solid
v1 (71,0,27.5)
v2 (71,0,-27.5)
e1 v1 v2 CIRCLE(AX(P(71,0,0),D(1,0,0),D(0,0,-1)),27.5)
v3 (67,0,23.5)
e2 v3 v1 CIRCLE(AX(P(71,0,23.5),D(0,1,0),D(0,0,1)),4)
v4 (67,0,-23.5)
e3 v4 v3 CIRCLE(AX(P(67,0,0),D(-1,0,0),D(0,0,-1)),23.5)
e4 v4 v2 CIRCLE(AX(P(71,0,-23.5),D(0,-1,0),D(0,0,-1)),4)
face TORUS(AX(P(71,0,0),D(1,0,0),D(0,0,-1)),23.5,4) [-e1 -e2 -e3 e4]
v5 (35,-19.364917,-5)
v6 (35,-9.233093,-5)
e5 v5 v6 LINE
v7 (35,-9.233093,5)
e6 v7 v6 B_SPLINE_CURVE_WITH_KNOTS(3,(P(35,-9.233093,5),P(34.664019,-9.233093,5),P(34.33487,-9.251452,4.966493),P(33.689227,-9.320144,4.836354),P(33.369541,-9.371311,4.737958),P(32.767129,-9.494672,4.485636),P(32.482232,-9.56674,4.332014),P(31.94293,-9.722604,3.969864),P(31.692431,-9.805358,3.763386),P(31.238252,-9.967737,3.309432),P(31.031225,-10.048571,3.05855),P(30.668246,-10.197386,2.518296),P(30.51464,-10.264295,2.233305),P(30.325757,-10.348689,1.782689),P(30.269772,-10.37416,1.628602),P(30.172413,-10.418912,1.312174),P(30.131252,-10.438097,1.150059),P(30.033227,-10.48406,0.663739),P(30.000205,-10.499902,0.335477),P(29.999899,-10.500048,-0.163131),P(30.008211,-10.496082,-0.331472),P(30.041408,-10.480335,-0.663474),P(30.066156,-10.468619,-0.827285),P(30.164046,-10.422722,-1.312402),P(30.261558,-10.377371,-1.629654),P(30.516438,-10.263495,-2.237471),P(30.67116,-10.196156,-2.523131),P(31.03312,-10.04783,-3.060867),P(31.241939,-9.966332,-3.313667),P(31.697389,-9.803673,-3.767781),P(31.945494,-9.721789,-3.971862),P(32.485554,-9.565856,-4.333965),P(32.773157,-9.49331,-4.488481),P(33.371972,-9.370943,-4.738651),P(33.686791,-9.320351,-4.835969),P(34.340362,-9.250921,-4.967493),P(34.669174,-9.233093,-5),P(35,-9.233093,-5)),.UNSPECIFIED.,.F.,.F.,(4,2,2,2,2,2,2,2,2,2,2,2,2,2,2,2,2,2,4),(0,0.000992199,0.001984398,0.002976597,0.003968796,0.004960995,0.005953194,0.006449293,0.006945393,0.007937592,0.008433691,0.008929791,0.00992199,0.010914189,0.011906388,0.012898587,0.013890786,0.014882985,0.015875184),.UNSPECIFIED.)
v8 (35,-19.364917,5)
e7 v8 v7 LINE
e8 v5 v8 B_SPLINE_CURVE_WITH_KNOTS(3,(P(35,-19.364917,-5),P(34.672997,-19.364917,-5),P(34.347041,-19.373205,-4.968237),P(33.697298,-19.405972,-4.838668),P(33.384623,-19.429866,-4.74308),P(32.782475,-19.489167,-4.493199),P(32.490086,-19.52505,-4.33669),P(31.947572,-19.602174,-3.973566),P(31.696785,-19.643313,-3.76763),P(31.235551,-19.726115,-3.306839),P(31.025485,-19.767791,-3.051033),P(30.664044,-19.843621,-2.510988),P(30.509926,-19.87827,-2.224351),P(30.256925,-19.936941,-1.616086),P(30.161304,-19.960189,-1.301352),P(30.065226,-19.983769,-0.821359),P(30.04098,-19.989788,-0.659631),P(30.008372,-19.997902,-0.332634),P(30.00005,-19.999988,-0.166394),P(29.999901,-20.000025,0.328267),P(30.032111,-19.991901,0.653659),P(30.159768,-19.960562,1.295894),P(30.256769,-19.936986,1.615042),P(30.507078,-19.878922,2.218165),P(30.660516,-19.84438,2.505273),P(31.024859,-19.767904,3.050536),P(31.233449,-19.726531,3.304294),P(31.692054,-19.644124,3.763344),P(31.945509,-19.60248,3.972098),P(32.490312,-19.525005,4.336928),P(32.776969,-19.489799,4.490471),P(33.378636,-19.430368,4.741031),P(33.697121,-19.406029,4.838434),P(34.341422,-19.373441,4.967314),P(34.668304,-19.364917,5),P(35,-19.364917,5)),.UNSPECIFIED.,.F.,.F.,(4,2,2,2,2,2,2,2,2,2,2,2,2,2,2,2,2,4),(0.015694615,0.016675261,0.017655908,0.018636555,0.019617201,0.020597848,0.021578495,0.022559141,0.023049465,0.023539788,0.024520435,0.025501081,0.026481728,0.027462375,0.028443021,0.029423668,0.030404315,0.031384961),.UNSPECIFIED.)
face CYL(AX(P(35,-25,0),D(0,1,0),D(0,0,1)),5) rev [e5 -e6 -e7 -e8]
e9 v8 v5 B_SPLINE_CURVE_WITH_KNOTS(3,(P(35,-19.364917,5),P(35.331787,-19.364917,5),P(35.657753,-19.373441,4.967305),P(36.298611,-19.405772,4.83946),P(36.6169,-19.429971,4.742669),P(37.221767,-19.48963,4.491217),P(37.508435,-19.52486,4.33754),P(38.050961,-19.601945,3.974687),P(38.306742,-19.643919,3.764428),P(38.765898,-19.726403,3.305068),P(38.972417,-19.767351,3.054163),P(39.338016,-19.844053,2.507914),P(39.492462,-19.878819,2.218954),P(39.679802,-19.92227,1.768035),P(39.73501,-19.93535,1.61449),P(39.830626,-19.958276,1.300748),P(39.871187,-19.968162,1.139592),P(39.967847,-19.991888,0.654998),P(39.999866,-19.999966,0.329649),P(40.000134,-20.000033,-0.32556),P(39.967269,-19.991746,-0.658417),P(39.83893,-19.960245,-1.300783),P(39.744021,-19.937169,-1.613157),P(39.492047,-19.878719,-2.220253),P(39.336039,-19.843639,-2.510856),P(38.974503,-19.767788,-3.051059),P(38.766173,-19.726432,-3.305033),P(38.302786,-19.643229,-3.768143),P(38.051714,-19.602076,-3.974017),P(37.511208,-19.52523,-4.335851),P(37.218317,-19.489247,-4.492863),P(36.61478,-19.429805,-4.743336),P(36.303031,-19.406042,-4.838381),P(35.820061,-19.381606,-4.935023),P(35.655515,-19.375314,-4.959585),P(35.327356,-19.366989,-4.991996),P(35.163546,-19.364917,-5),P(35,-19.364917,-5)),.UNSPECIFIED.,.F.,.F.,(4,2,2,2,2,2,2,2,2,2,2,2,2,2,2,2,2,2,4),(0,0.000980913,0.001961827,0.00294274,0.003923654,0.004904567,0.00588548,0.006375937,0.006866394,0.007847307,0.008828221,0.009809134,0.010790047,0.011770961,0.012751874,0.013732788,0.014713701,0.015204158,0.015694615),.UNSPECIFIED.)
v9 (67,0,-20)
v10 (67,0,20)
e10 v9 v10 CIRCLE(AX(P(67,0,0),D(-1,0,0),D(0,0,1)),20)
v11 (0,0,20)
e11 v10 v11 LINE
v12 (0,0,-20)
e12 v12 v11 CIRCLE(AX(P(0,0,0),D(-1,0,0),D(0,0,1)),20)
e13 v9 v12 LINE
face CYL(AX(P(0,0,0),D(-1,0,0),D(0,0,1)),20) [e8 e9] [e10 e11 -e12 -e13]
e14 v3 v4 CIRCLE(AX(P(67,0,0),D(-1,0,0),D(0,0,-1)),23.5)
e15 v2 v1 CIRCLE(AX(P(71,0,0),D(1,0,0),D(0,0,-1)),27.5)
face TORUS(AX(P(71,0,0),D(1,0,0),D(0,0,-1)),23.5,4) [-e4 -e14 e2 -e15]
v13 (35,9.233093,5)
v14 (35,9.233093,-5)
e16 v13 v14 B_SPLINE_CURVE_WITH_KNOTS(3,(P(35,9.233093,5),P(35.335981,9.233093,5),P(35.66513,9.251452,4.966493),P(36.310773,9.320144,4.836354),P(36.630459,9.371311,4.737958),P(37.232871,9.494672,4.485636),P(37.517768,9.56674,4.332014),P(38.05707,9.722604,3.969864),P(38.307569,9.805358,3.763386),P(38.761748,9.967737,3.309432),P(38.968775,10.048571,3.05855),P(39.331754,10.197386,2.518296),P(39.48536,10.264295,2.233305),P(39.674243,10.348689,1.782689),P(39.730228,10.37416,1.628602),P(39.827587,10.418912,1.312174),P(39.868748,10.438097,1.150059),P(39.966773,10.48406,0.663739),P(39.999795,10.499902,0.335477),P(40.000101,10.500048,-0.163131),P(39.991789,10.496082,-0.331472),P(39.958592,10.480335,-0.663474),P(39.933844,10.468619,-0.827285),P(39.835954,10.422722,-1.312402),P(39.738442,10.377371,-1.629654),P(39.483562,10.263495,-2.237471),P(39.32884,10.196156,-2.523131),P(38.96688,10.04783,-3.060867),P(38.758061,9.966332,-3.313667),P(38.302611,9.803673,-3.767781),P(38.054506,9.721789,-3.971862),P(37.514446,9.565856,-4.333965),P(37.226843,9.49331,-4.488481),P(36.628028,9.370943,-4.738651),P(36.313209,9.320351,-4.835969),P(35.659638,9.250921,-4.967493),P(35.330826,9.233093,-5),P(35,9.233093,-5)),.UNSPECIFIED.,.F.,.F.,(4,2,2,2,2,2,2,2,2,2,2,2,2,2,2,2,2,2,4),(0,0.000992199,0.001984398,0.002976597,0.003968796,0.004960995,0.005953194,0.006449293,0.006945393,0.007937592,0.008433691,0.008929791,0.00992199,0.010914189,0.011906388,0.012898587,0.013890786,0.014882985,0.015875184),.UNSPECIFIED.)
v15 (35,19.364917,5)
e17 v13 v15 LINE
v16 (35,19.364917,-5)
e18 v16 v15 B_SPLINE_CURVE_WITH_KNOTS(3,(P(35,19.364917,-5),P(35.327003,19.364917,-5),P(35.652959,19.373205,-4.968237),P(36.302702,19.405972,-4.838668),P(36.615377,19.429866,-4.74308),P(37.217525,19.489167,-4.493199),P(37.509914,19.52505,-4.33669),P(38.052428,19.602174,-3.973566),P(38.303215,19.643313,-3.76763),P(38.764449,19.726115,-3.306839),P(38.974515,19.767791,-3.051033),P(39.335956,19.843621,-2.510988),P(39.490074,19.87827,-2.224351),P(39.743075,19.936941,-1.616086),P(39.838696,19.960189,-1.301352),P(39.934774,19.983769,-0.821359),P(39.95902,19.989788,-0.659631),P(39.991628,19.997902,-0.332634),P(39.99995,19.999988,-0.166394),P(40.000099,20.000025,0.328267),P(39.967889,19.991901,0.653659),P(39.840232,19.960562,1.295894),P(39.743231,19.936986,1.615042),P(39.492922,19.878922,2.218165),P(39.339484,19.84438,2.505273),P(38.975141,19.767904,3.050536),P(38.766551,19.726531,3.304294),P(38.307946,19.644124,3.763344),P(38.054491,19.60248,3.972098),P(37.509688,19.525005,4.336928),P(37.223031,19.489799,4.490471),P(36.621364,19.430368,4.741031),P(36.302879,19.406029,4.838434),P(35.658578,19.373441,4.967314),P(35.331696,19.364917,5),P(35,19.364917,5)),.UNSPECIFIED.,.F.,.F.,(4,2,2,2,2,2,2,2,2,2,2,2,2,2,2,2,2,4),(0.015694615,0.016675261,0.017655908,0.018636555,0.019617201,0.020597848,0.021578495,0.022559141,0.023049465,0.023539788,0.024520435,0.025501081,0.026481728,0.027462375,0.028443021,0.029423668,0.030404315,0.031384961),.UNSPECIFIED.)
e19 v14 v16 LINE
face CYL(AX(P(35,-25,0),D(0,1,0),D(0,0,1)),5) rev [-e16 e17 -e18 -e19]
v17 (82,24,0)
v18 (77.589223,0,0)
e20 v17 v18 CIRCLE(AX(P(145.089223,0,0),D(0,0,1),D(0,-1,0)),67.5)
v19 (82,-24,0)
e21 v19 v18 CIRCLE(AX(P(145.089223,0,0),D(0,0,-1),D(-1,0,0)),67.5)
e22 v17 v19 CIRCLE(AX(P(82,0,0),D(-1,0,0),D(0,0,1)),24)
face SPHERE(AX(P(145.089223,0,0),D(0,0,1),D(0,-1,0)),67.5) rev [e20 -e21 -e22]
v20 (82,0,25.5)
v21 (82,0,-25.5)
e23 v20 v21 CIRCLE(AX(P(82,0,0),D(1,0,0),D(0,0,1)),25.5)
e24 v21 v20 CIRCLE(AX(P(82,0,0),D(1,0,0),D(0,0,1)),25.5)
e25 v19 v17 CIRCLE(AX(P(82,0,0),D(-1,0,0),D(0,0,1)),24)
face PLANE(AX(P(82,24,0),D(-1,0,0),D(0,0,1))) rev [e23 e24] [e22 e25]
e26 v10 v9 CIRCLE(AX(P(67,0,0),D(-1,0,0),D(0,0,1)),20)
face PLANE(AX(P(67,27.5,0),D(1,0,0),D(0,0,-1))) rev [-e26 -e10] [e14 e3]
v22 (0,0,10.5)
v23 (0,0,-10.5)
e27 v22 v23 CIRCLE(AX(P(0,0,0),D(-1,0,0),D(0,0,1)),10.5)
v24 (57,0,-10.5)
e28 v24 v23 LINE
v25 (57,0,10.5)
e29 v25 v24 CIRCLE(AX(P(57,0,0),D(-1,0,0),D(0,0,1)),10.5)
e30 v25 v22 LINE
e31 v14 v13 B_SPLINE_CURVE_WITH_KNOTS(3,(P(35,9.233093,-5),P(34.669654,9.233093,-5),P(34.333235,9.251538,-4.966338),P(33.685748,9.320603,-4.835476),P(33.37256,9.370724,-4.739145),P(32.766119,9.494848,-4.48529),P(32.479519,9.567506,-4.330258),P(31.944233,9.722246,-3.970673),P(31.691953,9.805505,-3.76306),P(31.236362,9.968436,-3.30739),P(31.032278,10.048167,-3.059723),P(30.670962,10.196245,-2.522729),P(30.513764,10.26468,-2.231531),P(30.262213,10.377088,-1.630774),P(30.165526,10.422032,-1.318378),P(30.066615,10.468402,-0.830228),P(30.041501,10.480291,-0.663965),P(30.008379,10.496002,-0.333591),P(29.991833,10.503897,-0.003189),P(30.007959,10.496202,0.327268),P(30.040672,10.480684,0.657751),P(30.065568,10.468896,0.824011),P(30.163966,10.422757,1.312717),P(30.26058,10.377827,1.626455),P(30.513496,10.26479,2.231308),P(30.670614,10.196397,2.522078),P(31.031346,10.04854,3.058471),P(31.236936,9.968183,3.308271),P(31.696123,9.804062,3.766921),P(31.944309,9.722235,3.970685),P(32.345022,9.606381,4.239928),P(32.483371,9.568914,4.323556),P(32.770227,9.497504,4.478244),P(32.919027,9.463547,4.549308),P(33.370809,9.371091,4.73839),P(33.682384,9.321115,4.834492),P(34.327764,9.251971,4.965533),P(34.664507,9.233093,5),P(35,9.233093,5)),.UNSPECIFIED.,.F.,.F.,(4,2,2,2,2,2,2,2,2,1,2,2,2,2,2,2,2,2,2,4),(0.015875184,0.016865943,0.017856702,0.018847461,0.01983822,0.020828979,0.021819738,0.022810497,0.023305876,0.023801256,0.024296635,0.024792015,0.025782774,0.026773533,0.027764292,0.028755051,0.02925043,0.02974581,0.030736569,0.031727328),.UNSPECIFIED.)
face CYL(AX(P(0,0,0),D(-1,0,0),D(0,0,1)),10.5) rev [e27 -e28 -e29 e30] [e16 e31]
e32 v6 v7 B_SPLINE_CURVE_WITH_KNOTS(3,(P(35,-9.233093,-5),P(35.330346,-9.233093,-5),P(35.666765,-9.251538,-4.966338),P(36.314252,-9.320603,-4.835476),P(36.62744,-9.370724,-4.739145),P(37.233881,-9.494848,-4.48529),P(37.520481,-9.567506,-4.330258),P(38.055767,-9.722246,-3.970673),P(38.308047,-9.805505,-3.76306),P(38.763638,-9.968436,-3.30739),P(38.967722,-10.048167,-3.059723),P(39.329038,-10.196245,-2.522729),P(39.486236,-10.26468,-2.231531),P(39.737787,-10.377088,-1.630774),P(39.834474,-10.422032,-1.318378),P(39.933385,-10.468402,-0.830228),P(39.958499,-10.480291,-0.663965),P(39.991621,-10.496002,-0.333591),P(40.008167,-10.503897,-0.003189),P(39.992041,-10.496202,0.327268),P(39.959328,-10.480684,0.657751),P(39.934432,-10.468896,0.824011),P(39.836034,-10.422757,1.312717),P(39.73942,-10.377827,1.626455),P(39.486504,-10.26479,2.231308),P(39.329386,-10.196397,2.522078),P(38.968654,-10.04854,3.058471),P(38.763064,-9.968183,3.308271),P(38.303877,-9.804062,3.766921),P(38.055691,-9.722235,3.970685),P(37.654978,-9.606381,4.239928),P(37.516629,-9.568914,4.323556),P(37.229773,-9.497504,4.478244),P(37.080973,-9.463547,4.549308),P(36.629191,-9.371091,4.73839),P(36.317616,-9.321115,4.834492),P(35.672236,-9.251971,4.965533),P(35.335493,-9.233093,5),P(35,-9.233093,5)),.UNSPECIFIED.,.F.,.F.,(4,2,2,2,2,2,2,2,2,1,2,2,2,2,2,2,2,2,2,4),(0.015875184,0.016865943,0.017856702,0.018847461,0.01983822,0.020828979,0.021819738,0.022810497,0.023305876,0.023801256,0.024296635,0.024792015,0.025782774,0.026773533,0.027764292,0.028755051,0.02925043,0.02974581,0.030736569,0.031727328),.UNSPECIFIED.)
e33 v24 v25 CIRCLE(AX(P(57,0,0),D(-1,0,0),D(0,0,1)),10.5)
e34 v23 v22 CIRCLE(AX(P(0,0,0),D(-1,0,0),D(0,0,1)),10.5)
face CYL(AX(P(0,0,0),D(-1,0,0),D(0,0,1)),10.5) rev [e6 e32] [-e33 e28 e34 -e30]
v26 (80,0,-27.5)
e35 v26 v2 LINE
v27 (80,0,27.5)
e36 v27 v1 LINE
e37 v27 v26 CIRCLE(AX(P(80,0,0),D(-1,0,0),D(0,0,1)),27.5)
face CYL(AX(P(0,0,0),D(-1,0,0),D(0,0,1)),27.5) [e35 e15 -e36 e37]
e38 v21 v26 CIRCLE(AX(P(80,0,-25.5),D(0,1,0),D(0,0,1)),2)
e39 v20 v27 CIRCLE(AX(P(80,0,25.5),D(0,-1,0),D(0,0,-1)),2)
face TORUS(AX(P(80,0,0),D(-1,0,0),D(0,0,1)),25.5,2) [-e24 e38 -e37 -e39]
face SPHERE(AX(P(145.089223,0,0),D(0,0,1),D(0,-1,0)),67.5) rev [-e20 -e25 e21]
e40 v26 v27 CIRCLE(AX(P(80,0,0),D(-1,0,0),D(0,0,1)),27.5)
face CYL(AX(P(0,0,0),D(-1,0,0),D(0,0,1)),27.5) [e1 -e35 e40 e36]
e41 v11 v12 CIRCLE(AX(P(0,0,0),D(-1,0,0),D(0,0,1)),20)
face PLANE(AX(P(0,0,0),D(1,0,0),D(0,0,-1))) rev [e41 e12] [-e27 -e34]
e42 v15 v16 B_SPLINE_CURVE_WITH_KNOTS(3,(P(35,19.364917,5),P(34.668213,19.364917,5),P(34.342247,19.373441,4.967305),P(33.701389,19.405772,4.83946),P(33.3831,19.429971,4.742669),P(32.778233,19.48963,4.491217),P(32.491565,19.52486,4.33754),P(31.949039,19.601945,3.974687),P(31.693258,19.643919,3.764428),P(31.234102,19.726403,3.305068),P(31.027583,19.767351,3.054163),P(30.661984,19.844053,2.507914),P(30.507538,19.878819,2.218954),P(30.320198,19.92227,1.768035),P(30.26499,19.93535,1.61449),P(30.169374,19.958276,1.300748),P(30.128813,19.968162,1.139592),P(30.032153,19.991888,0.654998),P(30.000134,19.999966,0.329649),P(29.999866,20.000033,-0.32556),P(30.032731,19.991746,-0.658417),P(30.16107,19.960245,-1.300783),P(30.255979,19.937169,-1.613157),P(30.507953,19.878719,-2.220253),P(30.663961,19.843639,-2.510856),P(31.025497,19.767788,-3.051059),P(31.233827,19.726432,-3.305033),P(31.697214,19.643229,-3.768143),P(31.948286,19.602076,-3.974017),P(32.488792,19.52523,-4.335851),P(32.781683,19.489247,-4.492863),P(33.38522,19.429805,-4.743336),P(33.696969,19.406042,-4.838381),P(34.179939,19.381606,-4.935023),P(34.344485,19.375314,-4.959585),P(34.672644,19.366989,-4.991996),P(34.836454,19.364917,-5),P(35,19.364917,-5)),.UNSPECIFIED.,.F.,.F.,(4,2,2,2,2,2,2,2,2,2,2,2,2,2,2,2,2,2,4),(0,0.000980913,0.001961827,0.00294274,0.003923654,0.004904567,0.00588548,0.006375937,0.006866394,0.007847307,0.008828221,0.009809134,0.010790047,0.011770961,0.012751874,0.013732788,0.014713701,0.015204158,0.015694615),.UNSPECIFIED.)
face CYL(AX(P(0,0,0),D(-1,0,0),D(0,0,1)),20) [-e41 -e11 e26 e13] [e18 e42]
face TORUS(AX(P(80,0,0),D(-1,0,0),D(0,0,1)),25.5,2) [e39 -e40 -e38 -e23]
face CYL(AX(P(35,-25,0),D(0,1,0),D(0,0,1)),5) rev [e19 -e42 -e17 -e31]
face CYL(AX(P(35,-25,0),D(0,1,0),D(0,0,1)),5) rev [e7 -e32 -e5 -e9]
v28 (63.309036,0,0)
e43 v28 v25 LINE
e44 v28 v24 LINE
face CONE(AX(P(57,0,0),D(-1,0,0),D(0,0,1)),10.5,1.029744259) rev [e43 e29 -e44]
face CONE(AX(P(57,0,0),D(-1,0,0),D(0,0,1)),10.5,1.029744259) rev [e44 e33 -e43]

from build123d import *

# Parameters (mm, degrees)
M24_TAPPED_HOLE1_D     = 21
M24_TAPPED_HOLE1_DEPTH = 57
M24_TAPPED_HOLE1_TIP   = 6.3090365
SKETCH4_R              = 5
CUT_EXTRUDE1_DEPTH     = 25
FILLET2_R              = 2
FILLET3_R              = 4


with BuildPart() as part:
    # Sketch1 → Revolve1 (revolve)
    with BuildSketch(Plane.XY, mode=Mode.PRIVATE) as revolve1_sk:
        with BuildLine():
            Line((67, 27.5), (67, 20))
            Line((67, 20), (0, 20))
            Line((0, 20), (0, 0))
            Line((0, 0), (77.589222534, 0))
            ThreePointArc((77.589222534, 0), (78.70107404, 12.20097289), (82, 24))
            Line((82, 24), (82, 27.5))
            Line((82, 27.5), (67, 27.5))
        make_face()
    revolve(revolve1_sk.sketch.rotate(Axis((0, 0, 0), (1, 0, 0)), 90), axis=Axis((0, 0, 0), (1, 0, 0)))

    # M24 Tapped Hole1
    with Locations(Plane.ZY):
        with Locations((0, 0)):
            Hole(M24_TAPPED_HOLE1_D / 2, depth=M24_TAPPED_HOLE1_DEPTH)
            with Locations((0, 0, -(M24_TAPPED_HOLE1_DEPTH + M24_TAPPED_HOLE1_TIP / 2))):  # 118° drill point
                Cone(0, M24_TAPPED_HOLE1_D / 2, M24_TAPPED_HOLE1_TIP, mode=Mode.SUBTRACT)

    # Sketch4 → Cut-Extrude1 (cut, symmetric)
    with BuildSketch(Plane(origin=(0, 0, 0), x_dir=(1, 0, 0), z_dir=(0, 1, 0))):
        with Locations(Location((35, 0, 0), (0, 0, 270))):
            Circle(SKETCH4_R)
    extrude(amount=CUT_EXTRUDE1_DEPTH, both=True, mode=Mode.SUBTRACT)

    # Fillet2
    fillet2_edges = [part.edges().sort_by_distance(p)[0] for p in [
        (82, 0, -27.5),
    ]]
    fillet(fillet2_edges, radius=FILLET2_R)

    # Fillet3
    fillet3_edges = [part.edges().sort_by_distance(p)[0] for p in [
        (67, 0, -27.5),
    ]]
    fillet(fillet3_edges, radius=FILLET3_R)


solid = part.part
